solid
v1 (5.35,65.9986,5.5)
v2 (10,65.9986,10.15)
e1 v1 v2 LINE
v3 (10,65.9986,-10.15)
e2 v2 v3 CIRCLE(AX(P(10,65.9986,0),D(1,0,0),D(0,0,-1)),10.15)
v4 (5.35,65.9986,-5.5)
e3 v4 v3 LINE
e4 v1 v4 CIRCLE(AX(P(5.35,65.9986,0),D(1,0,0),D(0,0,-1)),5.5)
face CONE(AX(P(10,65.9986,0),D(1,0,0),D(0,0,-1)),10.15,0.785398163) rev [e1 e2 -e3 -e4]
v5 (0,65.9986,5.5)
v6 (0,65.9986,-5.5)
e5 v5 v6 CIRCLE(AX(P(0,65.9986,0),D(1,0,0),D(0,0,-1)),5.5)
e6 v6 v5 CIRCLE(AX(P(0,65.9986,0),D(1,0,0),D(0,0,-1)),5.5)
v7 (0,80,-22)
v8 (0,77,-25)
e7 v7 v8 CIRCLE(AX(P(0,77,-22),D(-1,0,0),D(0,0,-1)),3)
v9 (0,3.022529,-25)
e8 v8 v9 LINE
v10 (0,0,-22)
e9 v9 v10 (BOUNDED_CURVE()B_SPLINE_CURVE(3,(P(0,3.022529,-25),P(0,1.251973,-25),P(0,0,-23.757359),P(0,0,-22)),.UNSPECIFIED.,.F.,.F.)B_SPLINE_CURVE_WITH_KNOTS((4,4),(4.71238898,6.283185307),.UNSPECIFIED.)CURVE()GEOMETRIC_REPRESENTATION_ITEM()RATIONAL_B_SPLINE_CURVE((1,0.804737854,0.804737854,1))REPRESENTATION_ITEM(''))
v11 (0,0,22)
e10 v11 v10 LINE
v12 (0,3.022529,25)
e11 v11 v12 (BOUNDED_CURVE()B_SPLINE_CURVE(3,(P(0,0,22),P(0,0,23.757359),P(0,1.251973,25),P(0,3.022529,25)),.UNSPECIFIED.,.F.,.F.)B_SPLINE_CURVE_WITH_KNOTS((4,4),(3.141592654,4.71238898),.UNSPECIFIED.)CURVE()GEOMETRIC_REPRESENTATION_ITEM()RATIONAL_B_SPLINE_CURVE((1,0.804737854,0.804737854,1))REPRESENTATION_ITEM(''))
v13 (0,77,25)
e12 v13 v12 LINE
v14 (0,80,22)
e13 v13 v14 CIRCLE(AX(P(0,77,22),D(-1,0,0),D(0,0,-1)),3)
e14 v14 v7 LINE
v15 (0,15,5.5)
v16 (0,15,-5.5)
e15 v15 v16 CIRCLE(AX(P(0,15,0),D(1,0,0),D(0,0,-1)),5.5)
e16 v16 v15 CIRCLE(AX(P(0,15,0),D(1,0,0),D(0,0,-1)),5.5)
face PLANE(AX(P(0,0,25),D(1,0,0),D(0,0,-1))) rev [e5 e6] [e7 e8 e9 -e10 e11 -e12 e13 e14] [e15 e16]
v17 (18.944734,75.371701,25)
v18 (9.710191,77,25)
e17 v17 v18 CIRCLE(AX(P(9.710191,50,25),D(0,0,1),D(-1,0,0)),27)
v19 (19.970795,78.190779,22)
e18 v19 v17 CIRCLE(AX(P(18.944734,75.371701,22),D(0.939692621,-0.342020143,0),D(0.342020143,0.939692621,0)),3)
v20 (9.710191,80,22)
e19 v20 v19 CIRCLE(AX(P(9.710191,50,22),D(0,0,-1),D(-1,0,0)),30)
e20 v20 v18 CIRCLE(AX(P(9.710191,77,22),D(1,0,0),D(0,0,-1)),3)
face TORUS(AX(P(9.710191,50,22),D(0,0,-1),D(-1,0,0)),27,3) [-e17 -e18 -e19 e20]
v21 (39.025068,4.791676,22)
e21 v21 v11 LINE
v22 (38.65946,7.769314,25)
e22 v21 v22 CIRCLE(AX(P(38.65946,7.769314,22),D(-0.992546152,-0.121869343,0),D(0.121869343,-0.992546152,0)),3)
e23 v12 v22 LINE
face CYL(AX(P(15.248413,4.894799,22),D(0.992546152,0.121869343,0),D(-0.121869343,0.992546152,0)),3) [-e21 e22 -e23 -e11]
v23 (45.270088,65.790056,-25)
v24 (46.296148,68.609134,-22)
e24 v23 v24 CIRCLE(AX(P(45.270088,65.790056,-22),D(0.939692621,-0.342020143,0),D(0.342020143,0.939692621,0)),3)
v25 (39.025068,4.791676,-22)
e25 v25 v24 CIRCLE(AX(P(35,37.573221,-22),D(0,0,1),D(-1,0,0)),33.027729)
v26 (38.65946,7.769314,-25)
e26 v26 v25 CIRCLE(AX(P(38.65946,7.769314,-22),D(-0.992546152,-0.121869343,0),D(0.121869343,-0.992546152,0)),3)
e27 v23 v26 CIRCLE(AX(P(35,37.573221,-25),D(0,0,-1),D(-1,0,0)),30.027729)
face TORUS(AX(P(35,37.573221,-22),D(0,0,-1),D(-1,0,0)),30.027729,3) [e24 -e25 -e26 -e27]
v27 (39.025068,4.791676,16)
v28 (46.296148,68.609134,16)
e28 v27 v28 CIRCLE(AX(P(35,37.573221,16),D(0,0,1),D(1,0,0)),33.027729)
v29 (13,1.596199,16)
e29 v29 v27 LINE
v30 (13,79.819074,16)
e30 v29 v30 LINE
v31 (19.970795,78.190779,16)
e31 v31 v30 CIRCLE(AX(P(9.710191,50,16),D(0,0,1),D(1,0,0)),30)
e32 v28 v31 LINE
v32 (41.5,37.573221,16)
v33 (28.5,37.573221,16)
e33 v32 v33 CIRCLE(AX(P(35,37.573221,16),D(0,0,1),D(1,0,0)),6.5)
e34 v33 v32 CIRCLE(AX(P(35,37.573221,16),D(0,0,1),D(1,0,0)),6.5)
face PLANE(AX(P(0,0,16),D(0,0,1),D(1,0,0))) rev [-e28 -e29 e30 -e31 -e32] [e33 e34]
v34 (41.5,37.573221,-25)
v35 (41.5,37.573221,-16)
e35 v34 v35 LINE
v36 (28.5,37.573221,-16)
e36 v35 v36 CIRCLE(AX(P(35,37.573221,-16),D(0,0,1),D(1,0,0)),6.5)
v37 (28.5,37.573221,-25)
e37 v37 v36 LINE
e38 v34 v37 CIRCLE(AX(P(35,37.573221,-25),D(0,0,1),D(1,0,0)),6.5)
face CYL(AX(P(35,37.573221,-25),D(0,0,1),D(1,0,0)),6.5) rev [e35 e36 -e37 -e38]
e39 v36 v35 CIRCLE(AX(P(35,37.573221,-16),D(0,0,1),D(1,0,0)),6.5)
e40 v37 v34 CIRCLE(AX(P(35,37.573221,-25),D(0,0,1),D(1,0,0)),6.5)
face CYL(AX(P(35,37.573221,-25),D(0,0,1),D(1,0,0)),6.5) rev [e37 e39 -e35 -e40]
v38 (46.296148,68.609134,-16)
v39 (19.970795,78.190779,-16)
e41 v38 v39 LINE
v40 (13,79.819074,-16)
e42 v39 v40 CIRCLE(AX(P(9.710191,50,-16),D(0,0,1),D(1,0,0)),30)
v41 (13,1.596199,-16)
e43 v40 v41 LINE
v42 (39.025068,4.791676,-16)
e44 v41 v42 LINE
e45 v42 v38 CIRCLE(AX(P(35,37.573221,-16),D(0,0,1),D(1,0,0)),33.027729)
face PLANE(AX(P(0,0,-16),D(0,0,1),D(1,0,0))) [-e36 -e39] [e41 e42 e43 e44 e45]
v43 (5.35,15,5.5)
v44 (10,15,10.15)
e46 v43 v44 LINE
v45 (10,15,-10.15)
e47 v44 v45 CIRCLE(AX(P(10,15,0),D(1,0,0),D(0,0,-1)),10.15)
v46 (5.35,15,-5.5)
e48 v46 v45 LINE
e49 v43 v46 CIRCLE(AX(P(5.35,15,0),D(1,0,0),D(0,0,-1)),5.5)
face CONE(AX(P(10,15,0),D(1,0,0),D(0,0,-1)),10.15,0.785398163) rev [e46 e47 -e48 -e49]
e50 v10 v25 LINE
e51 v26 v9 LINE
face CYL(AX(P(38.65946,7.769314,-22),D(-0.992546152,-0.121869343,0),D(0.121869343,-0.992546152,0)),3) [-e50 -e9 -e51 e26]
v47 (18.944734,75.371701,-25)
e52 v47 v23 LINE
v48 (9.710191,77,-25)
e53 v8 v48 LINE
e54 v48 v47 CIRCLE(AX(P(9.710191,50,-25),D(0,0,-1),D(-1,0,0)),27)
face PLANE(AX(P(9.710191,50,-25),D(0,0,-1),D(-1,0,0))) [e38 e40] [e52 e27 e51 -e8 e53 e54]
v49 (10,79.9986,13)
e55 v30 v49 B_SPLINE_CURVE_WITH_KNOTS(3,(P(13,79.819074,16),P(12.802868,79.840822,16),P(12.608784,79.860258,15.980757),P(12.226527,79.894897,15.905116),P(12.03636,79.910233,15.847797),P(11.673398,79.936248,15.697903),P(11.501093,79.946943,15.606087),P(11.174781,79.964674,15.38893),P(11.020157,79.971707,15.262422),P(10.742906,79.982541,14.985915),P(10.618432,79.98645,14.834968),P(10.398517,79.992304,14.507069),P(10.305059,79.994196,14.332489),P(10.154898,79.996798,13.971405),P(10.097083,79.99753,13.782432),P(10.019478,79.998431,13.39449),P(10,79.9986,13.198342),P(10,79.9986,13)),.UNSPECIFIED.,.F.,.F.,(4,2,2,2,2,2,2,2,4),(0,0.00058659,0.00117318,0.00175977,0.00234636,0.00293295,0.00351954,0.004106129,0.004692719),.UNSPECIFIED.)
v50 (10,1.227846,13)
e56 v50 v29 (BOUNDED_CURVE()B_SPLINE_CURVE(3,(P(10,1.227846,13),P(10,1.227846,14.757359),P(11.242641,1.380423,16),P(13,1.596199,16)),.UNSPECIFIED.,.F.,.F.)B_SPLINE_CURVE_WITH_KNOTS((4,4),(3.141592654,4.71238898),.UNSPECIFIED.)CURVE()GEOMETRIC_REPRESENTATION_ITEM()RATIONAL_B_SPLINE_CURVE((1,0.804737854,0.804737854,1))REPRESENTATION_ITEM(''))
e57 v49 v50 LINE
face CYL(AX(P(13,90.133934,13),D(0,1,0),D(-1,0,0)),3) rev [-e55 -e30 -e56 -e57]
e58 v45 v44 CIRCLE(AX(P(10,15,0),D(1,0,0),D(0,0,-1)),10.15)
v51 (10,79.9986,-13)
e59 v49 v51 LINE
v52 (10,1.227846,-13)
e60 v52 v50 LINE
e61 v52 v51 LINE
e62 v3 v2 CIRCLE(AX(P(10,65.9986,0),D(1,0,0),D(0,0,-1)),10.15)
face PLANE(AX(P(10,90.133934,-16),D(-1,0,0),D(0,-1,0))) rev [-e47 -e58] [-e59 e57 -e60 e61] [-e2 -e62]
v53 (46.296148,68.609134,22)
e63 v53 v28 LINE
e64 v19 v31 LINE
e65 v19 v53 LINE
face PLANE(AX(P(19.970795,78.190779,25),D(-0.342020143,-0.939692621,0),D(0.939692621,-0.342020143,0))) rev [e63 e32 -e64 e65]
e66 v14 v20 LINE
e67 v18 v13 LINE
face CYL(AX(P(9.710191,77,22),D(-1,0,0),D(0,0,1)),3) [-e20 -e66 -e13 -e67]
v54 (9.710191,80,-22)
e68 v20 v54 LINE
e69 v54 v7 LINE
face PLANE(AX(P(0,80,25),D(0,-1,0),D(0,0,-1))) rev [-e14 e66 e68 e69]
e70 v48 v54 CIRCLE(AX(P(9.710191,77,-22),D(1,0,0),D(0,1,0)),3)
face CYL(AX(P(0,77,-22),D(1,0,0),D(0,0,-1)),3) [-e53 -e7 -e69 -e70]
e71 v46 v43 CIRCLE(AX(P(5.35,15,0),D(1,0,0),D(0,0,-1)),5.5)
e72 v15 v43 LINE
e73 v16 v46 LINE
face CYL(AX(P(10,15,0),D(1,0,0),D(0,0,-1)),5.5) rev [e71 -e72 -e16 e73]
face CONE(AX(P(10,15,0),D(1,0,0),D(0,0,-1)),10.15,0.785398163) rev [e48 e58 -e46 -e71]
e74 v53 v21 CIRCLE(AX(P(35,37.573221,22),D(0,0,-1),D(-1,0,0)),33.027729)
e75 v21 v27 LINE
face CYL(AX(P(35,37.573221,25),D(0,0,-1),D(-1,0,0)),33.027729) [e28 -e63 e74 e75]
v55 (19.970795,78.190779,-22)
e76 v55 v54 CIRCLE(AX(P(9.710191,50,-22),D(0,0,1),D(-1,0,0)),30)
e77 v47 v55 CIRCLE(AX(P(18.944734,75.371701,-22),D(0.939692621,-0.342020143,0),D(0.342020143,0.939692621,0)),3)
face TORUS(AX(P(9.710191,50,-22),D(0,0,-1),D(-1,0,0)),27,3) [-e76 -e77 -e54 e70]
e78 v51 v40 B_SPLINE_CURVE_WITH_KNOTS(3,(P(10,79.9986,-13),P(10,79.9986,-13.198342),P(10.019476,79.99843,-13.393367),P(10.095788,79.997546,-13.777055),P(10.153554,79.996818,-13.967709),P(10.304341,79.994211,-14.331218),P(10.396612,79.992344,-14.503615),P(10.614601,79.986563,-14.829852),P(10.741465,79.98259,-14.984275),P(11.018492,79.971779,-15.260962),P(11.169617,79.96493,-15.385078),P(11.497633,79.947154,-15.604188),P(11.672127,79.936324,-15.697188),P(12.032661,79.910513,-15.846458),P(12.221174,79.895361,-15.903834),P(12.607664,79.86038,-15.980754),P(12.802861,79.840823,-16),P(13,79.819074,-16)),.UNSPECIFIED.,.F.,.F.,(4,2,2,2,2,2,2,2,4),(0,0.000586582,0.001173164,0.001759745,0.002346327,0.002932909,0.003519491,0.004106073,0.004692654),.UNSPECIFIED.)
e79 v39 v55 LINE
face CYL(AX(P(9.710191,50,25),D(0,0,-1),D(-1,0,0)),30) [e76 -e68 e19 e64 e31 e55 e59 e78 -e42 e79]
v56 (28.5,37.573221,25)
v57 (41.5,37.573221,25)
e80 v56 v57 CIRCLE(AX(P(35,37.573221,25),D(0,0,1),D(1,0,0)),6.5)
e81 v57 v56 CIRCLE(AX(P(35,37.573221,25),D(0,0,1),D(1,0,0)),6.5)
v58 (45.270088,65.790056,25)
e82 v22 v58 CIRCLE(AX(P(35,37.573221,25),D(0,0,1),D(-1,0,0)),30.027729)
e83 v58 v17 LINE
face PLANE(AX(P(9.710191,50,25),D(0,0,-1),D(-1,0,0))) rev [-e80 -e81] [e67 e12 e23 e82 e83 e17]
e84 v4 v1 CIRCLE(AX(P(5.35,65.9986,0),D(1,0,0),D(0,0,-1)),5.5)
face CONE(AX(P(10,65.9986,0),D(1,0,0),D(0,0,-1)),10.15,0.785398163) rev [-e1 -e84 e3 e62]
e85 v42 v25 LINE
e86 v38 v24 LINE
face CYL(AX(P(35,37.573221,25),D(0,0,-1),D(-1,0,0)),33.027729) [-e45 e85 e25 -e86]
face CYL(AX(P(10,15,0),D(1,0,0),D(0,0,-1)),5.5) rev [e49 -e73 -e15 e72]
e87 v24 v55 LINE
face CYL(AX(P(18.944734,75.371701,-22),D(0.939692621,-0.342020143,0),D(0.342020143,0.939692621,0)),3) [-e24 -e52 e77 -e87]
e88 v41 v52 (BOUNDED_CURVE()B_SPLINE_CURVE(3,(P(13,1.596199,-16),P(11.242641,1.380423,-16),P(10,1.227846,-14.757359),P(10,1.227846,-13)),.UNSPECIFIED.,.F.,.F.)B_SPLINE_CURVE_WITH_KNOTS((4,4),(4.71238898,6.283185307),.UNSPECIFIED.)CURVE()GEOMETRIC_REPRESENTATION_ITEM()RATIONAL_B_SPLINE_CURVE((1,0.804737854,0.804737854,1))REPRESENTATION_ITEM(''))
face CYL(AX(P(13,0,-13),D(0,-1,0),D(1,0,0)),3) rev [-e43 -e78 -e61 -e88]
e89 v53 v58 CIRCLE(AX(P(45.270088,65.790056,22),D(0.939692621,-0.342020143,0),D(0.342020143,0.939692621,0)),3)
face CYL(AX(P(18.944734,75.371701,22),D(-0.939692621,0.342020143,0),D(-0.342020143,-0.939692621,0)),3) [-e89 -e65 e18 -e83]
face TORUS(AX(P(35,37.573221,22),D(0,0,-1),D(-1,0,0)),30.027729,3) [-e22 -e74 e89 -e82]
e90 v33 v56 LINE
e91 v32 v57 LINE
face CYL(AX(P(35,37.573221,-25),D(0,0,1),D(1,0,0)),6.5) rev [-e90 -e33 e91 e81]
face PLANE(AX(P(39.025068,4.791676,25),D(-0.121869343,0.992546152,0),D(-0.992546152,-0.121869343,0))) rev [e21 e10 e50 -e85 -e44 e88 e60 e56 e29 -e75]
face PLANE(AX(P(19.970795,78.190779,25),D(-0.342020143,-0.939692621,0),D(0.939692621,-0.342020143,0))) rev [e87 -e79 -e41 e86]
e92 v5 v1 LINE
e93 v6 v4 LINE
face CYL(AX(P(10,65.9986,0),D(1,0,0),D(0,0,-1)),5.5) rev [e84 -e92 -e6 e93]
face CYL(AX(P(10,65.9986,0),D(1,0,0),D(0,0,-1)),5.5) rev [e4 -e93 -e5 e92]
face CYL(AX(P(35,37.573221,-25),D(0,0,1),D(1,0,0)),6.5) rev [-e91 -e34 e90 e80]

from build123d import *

# Parameters (mm, degrees)
EXTRUDE_1_DEPTH          = 25
SKETCH_3_W               = 68.112999437
SKETCH_3_H               = 98.020483962
CUT_EXTRUDE_1_DEPTH      = 16
SKETCH_4_R               = 6.5
CUT_EXTRUDE_2_DEPTH      = 117.308950023
FILLET_1_R               = 3
HOLE_WIZARD_1_AT_2_COUNT = 2
HOLE_WIZARD_1_AT_2_PITCH = 50.998600142
FILLET_2_R               = 3


with BuildPart() as part:
    # 草图2 → 凸台-拉伸1 (new, symmetric)
    with BuildSketch(Plane.XY):
        with BuildLine():
            Line((0, 0), (0, 80))
            Line((0, 80), (9.710190579, 80))
            ThreePointArc((9.710190579, 80), (14.919635909, 79.54423259), (19.970794879, 78.190778624))
            Line((19.970794879, 78.190778624), (46.296148462, 68.609133513))
            ThreePointArc((46.296148462, 68.609133513), (67.815421572, 33.834375668), (39.025067596, 4.791675789))
            Line((39.025067596, 4.791675789), (0, 0))
        make_face()
    extrude(amount=EXTRUDE_1_DEPTH, both=True)

    # 草图3 → 切除-拉伸1 (cut, symmetric)
    with BuildSketch(Plane.XY):
        with Locations((44.056499718, 41.123691615)):
            Rectangle(SKETCH_3_W, SKETCH_3_H)
    extrude(amount=CUT_EXTRUDE_1_DEPTH, both=True, mode=Mode.SUBTRACT)

    # 草图4 → 切除-拉伸2 (cut, through all)
    with BuildSketch(Plane.XY.offset(25)):
        with Locations((35, 37.573220687)):
            Circle(SKETCH_4_R)
    extrude(amount=-CUT_EXTRUDE_2_DEPTH, mode=Mode.SUBTRACT)

    # 圆角1
    fillet_1_edges = [part.edges().sort_by_distance(p)[0] for p in [
        (33.13347167, 73.399956068, 25),
        (14.919635909, 79.54423259, 25),
        (4.855095289, 80, 25),
        (19.512533798, 2.395837894, 25),
        (4.855095289, 80, -25),
        (14.919635909, 79.54423259, -25),
        (67.815421572, 33.834375668, 25),
        (33.13347167, 73.399956068, -25),
        (67.815421572, 33.834375668, -25),
        (19.512533798, 2.395837894, -25),
    ]]
    fillet(fillet_1_edges, radius=FILLET_1_R)

    # 草图6 → 打孔尺寸(%根据)内六角花形半沉头螺钉的类型1 (revolve, cut)
    with BuildSketch(Plane(origin=(10, 65.998600142, 0), x_dir=(0, 0, -1), z_dir=(0, 1, 0))):
        Polygon((0, 0), (0, 10), (5.5, 10), (5.5, 4.65), (10.15, 0), align=None)
    hole_wizard_1 = revolve(axis=Axis((16.35, 65.998600142, 0), (-1, 0, 0)), mode=Mode.SUBTRACT)

    # 打孔尺寸(%根据)内六角花形半沉头螺钉的类型1 at 2: 打孔尺寸(%根据)内六角花形半沉头螺钉的类型1 ×2
    with Locations(*[(0, -i * HOLE_WIZARD_1_AT_2_PITCH, 0) for i in range(1, HOLE_WIZARD_1_AT_2_COUNT)]):
        add(hole_wizard_1, mode=Mode.SUBTRACT)

    # 圆角2
    fillet_2_edges = [part.edges().sort_by_distance(p)[0] for p in [
        (10, 40.613222876, -16),
        (10, 40.613222876, 16),
    ]]
    fillet(fillet_2_edges, radius=FILLET_2_R)


solid = part.part
